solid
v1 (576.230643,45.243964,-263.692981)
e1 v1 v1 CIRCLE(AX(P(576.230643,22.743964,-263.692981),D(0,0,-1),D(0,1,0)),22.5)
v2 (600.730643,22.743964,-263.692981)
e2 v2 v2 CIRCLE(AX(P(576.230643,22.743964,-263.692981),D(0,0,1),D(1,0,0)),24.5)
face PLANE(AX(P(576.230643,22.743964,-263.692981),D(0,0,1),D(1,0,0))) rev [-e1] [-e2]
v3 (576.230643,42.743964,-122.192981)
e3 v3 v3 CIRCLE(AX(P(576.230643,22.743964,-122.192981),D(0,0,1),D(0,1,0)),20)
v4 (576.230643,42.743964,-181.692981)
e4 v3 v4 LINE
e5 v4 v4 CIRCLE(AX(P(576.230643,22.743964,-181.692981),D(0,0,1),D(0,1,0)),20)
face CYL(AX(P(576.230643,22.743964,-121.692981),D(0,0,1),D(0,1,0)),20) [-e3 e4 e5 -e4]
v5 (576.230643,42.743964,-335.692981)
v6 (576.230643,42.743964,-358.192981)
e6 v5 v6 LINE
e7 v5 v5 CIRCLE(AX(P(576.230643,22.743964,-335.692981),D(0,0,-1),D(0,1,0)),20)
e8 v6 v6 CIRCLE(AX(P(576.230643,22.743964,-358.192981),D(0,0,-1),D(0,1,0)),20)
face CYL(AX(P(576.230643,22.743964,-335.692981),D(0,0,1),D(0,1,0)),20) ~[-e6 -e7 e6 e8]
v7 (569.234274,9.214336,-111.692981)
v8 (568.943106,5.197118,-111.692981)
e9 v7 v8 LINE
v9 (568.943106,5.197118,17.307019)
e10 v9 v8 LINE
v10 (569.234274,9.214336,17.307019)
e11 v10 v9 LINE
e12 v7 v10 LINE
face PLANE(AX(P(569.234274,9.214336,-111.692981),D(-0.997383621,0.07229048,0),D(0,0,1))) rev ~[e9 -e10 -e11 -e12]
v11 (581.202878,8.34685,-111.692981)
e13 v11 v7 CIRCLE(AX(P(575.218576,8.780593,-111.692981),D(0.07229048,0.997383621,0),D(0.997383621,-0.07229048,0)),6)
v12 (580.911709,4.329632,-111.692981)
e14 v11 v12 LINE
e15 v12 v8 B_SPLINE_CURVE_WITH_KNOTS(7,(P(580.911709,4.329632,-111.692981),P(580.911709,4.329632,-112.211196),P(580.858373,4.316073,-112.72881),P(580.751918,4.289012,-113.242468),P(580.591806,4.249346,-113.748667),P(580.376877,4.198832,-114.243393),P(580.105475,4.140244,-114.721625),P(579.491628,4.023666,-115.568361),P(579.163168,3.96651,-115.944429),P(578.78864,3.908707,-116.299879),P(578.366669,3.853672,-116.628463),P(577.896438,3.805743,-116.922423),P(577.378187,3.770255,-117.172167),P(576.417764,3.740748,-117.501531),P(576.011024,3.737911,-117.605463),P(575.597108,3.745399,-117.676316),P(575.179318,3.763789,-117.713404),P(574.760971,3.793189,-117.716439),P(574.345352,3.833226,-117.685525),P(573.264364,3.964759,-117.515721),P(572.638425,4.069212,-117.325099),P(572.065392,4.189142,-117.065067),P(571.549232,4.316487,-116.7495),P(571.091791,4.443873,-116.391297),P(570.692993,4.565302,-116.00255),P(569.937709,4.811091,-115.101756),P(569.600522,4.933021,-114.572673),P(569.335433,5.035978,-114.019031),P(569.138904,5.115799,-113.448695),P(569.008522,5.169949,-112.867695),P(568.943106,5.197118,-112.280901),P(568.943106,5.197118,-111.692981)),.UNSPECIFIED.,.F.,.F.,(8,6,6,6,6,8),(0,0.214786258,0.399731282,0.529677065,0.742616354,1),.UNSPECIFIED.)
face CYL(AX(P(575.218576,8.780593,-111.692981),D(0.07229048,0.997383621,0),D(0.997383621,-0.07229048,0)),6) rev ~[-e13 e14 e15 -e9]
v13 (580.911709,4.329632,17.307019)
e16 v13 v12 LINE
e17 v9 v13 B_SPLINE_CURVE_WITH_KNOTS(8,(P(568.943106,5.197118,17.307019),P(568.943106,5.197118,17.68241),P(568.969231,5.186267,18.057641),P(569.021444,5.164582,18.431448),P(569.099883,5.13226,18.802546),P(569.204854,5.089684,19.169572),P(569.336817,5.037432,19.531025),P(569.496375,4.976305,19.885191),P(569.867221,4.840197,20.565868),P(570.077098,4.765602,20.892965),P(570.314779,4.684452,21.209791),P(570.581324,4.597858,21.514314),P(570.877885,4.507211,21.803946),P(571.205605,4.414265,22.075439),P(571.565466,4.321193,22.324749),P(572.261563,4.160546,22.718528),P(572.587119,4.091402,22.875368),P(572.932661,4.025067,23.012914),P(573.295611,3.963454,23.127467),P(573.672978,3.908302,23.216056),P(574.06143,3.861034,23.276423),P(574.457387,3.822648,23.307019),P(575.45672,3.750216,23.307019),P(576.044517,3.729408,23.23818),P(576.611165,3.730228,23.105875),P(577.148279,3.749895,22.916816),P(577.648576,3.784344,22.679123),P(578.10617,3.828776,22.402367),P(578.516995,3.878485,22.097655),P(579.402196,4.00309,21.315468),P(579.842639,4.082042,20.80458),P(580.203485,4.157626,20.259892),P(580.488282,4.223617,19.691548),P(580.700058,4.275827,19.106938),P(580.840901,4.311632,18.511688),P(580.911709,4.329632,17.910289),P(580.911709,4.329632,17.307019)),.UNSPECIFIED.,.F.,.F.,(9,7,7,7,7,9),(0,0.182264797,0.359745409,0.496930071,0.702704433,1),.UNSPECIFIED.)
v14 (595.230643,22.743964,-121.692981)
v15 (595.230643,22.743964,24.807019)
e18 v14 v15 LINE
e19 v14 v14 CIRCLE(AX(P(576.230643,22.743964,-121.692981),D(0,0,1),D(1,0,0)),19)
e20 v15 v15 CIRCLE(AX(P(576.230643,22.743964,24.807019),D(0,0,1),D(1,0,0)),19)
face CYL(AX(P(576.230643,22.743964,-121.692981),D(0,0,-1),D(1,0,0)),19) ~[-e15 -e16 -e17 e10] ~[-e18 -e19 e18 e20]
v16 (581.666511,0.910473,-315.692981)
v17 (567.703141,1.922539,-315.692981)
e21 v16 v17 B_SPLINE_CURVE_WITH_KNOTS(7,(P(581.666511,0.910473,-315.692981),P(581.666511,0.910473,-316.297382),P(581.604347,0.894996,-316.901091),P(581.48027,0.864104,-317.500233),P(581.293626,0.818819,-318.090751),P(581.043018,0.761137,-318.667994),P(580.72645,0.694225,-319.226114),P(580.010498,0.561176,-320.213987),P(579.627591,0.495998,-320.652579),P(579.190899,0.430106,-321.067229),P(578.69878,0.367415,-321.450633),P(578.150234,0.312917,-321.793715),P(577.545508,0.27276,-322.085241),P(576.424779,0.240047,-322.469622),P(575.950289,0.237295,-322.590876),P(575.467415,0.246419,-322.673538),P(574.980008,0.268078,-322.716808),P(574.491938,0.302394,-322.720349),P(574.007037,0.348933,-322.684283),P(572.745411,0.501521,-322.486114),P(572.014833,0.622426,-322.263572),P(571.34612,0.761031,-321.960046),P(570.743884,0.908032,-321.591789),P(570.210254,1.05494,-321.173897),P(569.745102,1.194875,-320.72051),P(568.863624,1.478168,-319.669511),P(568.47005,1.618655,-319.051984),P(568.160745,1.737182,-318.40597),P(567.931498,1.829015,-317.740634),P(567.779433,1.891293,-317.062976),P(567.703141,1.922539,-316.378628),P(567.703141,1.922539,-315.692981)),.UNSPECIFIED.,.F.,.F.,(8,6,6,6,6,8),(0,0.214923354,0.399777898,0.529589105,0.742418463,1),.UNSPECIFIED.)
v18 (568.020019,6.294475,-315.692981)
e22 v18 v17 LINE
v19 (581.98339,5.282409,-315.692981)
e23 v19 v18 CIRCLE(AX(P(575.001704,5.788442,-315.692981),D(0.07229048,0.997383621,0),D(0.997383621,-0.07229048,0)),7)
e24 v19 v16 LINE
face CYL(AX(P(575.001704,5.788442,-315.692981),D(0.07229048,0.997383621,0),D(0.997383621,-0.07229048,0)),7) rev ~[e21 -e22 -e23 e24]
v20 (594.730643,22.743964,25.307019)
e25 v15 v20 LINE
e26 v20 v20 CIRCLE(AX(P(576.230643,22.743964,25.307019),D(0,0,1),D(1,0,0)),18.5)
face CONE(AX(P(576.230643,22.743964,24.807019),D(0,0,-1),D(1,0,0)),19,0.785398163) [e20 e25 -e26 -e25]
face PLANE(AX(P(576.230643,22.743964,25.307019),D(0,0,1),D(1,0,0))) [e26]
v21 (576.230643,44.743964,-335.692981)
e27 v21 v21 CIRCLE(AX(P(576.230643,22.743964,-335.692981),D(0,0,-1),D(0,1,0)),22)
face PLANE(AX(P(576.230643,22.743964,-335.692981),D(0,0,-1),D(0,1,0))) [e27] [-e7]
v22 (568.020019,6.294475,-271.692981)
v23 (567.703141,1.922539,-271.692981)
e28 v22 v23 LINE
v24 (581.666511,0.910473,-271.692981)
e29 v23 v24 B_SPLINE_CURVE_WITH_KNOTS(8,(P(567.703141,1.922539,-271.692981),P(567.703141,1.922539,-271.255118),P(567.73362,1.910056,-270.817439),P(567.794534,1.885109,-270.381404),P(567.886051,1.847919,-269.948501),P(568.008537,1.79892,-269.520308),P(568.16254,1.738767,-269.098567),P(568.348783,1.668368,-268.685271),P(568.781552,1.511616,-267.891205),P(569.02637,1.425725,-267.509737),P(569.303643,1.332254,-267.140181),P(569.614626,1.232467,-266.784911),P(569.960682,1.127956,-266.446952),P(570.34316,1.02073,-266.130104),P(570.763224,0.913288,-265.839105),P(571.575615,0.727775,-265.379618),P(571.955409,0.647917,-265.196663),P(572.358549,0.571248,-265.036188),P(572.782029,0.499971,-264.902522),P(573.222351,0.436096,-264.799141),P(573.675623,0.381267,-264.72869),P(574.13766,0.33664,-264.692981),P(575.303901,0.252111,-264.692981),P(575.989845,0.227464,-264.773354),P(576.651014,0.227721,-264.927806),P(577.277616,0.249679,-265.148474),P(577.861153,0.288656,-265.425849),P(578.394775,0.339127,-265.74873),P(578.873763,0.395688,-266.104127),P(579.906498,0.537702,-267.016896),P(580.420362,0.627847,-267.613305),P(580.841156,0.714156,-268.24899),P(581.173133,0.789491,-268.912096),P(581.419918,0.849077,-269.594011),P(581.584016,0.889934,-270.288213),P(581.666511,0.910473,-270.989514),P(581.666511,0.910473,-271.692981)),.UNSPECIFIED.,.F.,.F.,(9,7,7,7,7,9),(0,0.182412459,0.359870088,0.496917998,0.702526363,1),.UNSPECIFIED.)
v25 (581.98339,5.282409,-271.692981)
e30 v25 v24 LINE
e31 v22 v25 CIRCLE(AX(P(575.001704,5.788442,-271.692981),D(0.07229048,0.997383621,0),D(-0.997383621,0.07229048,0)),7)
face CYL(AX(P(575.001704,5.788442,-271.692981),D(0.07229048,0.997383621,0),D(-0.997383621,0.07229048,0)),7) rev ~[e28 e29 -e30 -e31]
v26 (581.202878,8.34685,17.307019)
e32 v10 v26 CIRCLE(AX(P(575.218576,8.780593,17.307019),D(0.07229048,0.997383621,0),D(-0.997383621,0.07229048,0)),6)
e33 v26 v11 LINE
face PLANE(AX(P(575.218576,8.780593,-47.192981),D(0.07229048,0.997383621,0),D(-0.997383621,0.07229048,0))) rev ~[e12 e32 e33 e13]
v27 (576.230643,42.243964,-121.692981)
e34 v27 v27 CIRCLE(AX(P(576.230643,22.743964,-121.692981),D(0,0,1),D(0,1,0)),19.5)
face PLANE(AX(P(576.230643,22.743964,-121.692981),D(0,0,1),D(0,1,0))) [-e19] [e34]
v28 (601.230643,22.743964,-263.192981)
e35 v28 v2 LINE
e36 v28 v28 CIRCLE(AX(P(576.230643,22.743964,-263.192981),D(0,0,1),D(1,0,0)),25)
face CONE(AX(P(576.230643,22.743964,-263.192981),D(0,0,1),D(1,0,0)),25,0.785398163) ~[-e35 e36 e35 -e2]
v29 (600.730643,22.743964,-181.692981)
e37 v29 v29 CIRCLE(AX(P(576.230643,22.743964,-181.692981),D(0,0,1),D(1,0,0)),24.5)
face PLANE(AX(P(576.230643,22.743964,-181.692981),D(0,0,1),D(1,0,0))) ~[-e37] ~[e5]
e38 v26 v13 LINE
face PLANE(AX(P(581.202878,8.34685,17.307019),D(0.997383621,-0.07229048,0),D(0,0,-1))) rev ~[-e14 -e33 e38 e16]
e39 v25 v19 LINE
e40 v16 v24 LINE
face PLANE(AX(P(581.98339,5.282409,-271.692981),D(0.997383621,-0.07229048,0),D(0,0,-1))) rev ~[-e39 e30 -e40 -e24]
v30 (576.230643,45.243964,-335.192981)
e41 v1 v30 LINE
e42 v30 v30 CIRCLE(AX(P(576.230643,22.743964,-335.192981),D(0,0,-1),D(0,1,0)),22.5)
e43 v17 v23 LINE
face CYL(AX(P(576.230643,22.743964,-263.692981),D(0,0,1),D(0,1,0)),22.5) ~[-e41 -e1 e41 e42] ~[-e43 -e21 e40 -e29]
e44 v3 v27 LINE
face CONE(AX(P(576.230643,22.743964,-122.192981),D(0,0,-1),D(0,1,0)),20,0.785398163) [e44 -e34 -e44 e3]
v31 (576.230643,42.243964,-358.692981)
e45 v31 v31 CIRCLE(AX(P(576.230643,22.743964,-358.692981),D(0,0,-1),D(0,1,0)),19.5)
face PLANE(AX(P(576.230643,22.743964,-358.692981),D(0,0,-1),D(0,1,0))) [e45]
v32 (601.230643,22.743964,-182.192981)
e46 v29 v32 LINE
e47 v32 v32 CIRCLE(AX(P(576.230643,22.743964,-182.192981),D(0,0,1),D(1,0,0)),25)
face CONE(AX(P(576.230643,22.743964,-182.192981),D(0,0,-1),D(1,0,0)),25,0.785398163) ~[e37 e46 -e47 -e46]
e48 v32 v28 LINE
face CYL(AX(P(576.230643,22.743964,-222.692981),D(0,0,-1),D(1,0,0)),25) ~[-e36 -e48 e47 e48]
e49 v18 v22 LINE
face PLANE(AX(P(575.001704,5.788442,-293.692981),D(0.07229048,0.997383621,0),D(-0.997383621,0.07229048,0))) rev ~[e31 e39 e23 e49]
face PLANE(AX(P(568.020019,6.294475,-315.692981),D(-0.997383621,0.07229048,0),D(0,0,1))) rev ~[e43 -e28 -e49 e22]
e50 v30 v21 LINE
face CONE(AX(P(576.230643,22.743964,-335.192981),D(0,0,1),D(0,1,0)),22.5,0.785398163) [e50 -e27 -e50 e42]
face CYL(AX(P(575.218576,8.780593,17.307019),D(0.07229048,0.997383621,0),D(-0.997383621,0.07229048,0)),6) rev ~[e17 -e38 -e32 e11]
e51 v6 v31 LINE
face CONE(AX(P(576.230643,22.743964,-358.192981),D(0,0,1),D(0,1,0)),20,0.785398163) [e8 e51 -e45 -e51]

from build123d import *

# Parameters (mm, degrees)
SKETCH1_W               = 25
SKETCH1_H               = 82
SKETCH2_R               = 22.5
BOSS_EXTRUDE1_DEPTH     = 72
SKETCH3_R               = 20
BOSS_EXTRUDE2_DEPTH     = 23
BOSS_EXTRUDE3_START     = 60
SKETCH4_R               = 20
BOSS_EXTRUDE3_DEPTH     = 60
SKETCH5_R               = 19
BOSS_EXTRUDE4_DEPTH     = 147
CUT_EXTRUDE1_REACH      = 700.948
CUT_EXTRUDE1_END_RADIUS = 19
CUT_EXTRUDE2_REACH      = 700.916
CUT_EXTRUDE2_END_RADIUS = 22.5
CHAMFER1_SIZE           = 0.5


with BuildPart() as part:
    # Sketch1 → Revolve1 (revolve)
    with BuildSketch(Plane(origin=(0, 22.743963655, 0), x_dir=(1, 0, 0), z_dir=(0, 1, 0))):
        with Locations((588.730642584, 222.692981355)):
            Rectangle(SKETCH1_W, SKETCH1_H)
    revolve(axis=Axis((576.230642584, 22.743963655, -263.692981355), (0, 0, 1)))

    # Sketch2 → Boss-Extrude1 (add)
    with BuildSketch(Plane(origin=(0, 0, -263.692981355), x_dir=(-1, 0, 0), z_dir=(0, 0, -1))):
        with Locations(Location((-576.230642584, 22.743963655, 0), (0, 0, 90))):
            Circle(SKETCH2_R)
    extrude(amount=BOSS_EXTRUDE1_DEPTH)

    # Sketch3 → Boss-Extrude2 (add)
    with BuildSketch(Plane(origin=(0, 0, -335.692981355), x_dir=(-1, 0, 0), z_dir=(0, 0, -1))):
        with Locations(Location((-576.230642584, 22.743963655, 0), (0, 0, 90))):
            Circle(SKETCH3_R)
    extrude(amount=BOSS_EXTRUDE2_DEPTH)

    # Sketch4 → Boss-Extrude3 (add)
    with BuildSketch(Plane.XY.offset(-181.692981355).offset(BOSS_EXTRUDE3_START)):
        with Locations(Location((576.230642584, 22.743963655, 0), (0, 0, 90))):
            Circle(SKETCH4_R)
    extrude(amount=-BOSS_EXTRUDE3_DEPTH)

    # Sketch5 → Boss-Extrude4 (add)
    with BuildSketch(Plane.XY.offset(-121.692981355)):
        with Locations((576.230642584, 22.743963655)):
            Circle(SKETCH5_R)
    extrude(amount=BOSS_EXTRUDE4_DEPTH)

    # Cut-Extrude1: up to this cylinder (the profile starts inside it)
    cut_extrude1_end = Plane(origin=(576.230642584, 22.743963655, -47.192981), z_dir=(0, 0, -1)) * Cylinder(CUT_EXTRUDE1_END_RADIUS, 1440.896, mode=Mode.PRIVATE)
    # Sketch6 → Cut-Extrude1 (cut, up to the surface)
    with BuildSketch(Plane(origin=(3.63913505, 50.208736879, 0), x_dir=(-0.9973836205258134, 0.07229048005664619, 0), z_dir=(0.07229048005664619, 0.9973836205258134, 0)), mode=Mode.PRIVATE) as cut_extrude1_sk1:
        with BuildLine():
            Line((-579.078832508, 17.307018645), (-579.078832508, -111.692981355))
            ThreePointArc((-579.078832508, -111.692981355), (-573.078832508, -117.692981355), (-567.078832508, -111.692981355))
            Line((-567.078832508, -111.692981355), (-567.078832508, 17.307018645))
            ThreePointArc((-567.078832508, 17.307018645), (-573.078832508, 23.307018645), (-579.078832508, 17.307018645))
        make_face()
    cut_extrude1_tool1 = extrude(cut_extrude1_sk1.sketch, amount=-CUT_EXTRUDE1_REACH, mode=Mode.PRIVATE) & cut_extrude1_end
    add(cut_extrude1_tool1.solids().sort_by_distance((575.218576, 8.780593, -47.192981))[0], mode=Mode.SUBTRACT)

    # Cut-Extrude2: up to this cylinder (the profile starts inside it)
    cut_extrude2_end = Plane(origin=(576.230642584, 22.743963655, -293.692981), z_dir=(0, 0, 1)) * Cylinder(CUT_EXTRUDE2_END_RADIUS, 1447.832, mode=Mode.PRIVATE)
    # Sketch7 → Cut-Extrude2 (cut, up to the surface)
    with BuildSketch(Plane(origin=(3.42226361, 47.216586018, 0), x_dir=(-0.9973836205258134, 0.07229048005664619, 0), z_dir=(0.07229048005664619, 0.9973836205258134, 0)), mode=Mode.PRIVATE) as cut_extrude2_sk1:
        with BuildLine():
            Line((-580.078832508, -271.692981355), (-580.078832508, -315.692981355))
            ThreePointArc((-580.078832508, -315.692981355), (-573.078832508, -322.692981355), (-566.078832508, -315.692981355))
            Line((-566.078832508, -315.692981355), (-566.078832508, -271.692981355))
            ThreePointArc((-566.078832508, -271.692981355), (-573.078832508, -264.692981355), (-580.078832508, -271.692981355))
        make_face()
    cut_extrude2_tool1 = extrude(cut_extrude2_sk1.sketch, amount=-CUT_EXTRUDE2_REACH, mode=Mode.PRIVATE) & cut_extrude2_end
    add(cut_extrude2_tool1.solids().sort_by_distance((575.001704, 5.788442, -293.692981))[0], mode=Mode.SUBTRACT)

    # Chamfer1
    chamfer1_edges = [part.edges().sort_by_distance(p)[0] for p in [
        (576.230642584, 2.743963655, -358.692981355),
        (576.230642584, 2.743963655, -121.692981355),
        (557.230642584, 22.743963655, 25.307018645),
        (551.230642584, 22.743963655, -181.692981355),
        (551.230642584, 22.743963655, -263.692981355),
        (576.230642584, 0.243963655, -335.692981355),
    ]]
    chamfer(chamfer1_edges, length=CHAMFER1_SIZE)


solid = part.part
